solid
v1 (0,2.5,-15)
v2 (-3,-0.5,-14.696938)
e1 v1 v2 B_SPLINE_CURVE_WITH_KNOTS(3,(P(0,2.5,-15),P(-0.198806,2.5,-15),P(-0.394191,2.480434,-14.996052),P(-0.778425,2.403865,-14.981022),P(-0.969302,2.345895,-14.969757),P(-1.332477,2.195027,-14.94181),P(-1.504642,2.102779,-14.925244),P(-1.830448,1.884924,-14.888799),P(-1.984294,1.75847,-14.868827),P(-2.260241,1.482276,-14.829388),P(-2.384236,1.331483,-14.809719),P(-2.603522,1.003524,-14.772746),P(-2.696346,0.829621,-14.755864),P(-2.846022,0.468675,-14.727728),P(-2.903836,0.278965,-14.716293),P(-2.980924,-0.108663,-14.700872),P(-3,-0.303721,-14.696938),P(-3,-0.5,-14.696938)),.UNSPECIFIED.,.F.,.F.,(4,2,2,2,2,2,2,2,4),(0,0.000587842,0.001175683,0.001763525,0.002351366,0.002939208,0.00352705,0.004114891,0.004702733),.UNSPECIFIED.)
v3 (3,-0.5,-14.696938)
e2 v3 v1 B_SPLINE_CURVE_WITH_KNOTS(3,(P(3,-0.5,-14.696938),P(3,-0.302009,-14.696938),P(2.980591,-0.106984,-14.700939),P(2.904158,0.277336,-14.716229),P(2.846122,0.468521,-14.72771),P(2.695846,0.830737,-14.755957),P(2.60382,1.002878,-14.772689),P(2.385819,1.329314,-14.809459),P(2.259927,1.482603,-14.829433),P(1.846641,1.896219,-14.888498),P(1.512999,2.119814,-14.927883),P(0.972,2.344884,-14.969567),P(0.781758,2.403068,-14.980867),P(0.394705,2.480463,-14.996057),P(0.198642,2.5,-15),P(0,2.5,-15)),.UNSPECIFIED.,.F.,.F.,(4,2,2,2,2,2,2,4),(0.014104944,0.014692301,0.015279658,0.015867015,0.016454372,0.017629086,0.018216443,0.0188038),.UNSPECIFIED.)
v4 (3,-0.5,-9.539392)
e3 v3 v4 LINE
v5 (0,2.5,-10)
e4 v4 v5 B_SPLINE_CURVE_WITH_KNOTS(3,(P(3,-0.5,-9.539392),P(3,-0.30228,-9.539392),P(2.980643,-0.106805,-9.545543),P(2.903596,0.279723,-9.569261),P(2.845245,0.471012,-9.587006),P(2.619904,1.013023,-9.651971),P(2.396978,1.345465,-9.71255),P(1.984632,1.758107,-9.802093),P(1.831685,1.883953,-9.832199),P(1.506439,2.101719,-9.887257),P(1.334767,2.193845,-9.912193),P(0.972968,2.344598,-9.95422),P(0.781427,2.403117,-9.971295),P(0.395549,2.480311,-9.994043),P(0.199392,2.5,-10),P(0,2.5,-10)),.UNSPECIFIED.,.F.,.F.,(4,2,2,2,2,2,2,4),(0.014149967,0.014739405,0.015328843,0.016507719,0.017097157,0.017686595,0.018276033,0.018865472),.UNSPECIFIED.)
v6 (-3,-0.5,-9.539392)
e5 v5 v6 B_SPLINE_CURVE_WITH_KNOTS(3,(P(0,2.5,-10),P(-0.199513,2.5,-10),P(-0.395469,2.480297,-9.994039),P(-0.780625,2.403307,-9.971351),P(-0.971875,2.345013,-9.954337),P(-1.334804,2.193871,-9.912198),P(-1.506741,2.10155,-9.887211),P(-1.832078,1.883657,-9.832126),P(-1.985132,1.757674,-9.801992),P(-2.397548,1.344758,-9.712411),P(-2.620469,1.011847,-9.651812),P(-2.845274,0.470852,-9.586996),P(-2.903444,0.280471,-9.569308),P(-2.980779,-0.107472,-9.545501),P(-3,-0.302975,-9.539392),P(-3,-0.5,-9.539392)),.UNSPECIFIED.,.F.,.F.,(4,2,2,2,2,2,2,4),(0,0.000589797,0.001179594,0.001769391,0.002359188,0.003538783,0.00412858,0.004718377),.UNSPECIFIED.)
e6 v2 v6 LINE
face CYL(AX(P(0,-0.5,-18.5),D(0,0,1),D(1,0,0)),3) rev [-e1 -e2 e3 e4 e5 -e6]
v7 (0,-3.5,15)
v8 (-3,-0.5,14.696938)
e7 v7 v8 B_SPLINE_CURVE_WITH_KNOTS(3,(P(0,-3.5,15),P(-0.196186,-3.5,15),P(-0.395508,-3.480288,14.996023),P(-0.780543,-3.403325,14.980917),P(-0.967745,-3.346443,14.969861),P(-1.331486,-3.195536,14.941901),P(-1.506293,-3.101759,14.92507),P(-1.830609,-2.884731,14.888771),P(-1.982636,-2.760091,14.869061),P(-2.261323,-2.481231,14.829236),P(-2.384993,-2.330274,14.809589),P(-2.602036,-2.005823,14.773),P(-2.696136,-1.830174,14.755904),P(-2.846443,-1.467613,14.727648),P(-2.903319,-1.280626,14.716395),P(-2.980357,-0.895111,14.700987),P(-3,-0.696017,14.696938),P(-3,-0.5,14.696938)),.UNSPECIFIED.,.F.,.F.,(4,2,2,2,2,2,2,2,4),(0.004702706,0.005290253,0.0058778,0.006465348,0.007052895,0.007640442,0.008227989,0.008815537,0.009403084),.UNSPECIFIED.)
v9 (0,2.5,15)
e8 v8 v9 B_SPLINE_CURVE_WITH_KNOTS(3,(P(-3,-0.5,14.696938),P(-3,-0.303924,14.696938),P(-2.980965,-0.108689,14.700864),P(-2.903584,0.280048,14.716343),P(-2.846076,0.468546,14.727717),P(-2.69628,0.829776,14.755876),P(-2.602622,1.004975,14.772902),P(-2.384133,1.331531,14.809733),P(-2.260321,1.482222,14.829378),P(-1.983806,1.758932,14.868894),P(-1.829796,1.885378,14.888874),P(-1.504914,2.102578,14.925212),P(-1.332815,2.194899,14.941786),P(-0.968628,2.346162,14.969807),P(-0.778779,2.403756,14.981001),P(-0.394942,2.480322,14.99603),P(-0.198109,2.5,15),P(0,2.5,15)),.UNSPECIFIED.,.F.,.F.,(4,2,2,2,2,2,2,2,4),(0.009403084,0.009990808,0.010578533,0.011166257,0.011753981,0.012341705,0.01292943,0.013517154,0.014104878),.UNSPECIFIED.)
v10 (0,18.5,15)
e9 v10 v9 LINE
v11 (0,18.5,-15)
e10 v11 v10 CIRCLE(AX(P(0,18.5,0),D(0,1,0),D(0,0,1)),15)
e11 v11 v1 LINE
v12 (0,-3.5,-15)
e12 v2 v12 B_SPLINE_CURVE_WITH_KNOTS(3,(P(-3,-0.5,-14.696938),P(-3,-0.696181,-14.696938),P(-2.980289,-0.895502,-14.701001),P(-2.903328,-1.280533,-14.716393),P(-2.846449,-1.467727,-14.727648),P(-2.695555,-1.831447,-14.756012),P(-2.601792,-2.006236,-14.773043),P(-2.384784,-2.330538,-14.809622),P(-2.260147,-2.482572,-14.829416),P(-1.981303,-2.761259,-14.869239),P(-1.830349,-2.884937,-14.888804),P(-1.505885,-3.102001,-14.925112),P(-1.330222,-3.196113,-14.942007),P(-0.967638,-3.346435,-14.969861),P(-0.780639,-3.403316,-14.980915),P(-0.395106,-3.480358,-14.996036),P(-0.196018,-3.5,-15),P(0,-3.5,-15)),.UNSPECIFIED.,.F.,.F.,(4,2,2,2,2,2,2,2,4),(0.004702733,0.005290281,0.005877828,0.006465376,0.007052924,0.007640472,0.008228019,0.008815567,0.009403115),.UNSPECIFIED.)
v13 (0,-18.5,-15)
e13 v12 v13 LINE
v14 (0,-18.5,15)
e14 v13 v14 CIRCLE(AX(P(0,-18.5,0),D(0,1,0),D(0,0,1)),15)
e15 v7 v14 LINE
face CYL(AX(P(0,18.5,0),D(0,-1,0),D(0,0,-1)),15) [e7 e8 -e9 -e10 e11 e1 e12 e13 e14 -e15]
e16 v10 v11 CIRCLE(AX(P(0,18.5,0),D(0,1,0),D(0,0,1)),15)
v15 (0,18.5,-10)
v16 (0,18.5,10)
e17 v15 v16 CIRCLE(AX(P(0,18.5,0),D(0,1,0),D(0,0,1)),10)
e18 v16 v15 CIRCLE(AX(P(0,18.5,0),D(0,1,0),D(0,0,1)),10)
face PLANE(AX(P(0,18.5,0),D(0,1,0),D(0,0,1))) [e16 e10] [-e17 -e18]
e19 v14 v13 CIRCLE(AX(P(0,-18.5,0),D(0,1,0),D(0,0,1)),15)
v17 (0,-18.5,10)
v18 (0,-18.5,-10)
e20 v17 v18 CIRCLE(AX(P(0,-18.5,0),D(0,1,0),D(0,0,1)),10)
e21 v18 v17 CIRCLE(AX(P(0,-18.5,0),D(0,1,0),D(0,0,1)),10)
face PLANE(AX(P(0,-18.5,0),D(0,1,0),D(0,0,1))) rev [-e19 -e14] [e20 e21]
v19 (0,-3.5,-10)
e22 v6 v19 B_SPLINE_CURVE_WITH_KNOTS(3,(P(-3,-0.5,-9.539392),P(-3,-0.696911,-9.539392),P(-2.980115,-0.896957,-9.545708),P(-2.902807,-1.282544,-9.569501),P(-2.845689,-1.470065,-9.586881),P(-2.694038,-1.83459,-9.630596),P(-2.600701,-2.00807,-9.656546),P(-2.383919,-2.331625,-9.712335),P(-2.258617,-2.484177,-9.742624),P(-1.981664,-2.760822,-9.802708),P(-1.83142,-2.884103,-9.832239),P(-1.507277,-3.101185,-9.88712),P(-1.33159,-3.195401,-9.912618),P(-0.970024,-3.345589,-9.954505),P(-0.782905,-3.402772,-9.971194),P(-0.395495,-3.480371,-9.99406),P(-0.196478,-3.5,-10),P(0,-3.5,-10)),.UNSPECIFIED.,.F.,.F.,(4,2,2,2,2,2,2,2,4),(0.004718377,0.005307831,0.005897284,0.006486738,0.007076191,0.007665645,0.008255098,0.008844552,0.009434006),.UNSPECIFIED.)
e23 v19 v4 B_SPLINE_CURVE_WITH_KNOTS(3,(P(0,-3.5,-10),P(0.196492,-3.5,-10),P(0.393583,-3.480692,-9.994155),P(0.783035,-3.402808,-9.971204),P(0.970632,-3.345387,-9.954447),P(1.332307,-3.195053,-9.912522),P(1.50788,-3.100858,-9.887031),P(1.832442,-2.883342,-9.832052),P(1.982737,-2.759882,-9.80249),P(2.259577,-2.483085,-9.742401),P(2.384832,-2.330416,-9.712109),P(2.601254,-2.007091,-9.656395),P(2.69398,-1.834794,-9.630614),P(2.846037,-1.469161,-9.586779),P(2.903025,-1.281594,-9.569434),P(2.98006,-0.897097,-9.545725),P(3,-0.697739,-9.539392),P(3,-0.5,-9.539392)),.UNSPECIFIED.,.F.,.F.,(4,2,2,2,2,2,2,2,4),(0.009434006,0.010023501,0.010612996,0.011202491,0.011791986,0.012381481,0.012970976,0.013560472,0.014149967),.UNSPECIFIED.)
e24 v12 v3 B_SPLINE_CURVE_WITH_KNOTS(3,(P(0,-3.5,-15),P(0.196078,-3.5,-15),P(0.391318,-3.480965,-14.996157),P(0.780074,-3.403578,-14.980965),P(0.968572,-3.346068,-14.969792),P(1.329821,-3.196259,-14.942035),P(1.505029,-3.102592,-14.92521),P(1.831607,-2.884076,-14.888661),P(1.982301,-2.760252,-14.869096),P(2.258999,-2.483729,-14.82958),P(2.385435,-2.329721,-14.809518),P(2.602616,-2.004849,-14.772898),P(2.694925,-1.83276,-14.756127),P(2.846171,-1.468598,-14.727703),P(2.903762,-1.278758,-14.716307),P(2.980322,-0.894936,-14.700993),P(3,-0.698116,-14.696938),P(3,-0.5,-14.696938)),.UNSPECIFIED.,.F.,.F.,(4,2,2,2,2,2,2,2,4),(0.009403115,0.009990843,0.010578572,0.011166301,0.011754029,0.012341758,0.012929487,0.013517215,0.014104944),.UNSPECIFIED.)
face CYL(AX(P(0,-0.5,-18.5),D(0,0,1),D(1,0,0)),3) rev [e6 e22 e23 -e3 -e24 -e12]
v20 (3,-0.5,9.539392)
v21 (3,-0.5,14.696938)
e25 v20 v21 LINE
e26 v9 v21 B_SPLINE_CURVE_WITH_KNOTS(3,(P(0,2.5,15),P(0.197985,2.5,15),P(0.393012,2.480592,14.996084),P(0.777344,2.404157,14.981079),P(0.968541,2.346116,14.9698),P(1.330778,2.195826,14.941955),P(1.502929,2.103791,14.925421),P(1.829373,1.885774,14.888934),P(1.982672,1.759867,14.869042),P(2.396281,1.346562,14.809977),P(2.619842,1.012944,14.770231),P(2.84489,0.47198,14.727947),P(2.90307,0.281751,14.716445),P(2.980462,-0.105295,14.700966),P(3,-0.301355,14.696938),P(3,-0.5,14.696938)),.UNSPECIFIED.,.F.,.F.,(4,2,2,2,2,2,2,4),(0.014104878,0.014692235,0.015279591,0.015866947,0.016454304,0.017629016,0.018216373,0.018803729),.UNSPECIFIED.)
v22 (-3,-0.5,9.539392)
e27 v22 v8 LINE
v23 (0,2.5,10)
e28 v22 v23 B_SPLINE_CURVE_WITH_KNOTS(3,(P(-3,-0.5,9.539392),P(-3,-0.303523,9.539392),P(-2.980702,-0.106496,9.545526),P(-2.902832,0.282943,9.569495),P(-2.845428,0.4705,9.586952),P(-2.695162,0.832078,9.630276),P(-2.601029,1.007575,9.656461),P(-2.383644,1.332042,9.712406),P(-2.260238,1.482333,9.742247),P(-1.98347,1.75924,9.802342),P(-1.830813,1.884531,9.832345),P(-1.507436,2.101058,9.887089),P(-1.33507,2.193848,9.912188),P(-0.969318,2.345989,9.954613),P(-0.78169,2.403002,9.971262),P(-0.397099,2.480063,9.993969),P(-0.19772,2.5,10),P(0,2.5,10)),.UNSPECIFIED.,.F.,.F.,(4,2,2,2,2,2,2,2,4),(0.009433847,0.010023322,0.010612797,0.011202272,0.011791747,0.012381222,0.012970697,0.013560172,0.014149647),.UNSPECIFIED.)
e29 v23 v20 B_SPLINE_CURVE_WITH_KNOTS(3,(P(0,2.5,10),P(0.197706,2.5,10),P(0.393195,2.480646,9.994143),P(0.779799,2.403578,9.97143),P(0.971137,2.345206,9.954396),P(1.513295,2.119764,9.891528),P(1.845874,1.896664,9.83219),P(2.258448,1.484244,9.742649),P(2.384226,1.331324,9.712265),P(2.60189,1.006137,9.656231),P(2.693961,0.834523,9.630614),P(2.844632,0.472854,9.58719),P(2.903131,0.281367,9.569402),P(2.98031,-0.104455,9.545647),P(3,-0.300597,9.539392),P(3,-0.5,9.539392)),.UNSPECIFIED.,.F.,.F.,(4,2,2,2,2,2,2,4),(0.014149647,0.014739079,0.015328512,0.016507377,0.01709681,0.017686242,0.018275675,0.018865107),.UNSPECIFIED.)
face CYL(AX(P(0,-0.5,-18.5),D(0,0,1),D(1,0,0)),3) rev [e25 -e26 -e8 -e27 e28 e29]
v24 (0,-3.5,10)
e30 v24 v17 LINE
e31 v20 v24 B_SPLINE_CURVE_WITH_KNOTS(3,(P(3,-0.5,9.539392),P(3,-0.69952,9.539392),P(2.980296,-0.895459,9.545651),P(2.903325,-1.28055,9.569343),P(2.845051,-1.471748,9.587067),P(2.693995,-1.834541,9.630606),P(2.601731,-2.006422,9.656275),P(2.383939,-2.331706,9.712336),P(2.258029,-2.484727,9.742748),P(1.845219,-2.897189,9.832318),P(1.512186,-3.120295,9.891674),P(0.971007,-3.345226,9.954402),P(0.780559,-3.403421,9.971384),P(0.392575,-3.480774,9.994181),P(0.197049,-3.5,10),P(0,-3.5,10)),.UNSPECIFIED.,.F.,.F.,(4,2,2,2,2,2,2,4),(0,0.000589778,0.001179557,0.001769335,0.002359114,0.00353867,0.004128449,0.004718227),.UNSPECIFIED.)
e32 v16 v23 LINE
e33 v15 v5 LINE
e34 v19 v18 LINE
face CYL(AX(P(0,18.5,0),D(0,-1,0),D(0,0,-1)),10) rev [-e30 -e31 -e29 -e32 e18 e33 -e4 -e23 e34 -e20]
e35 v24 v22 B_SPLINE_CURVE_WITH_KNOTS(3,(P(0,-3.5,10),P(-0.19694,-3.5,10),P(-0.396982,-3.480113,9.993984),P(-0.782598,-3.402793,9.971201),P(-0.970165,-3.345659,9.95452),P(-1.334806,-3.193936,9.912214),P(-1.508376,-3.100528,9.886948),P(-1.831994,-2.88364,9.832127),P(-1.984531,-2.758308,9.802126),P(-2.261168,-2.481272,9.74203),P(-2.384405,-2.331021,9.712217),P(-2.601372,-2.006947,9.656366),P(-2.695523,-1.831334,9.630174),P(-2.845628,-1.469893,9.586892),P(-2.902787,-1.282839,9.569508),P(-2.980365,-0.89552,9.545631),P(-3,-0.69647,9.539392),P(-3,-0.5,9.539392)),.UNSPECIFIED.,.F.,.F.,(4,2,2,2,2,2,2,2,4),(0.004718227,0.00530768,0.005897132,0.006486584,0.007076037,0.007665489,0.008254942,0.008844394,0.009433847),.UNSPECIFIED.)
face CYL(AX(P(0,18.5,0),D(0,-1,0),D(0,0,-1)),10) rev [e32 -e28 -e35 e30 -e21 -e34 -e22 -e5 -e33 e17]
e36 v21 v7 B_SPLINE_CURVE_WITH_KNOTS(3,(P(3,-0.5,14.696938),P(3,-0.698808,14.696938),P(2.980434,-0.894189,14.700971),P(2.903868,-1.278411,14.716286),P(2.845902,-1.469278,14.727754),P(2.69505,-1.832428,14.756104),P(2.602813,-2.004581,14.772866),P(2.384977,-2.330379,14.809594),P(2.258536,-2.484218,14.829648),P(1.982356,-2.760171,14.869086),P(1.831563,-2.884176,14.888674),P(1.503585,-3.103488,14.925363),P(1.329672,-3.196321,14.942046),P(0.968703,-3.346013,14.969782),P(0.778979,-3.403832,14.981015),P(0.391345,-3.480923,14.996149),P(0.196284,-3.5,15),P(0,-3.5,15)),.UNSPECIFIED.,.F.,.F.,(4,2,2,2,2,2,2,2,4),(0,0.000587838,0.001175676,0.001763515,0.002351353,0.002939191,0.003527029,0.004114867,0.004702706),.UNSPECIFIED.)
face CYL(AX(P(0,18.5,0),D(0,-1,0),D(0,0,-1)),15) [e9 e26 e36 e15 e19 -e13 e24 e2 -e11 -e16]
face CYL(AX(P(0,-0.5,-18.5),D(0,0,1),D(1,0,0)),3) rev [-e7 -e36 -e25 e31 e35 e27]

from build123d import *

# Parameters (mm, degrees)
BUSH_RING_PROFILE_SKETCH_R   = 15
BUSH_RING_PROFILE_SKETCH_R_2 = 10
BUSH_BODY_30X_20X37_DEPTH    = 18.5
CROSS_HOLE_SKETCH_R          = 3
CROSS_HOLE_6_DEPTH           = 18.5


with BuildPart() as part:
    # Bush Ring Profile Sketch → Bush Body Ø30xØ20x37 (new, symmetric)
    with BuildSketch(Plane(origin=(0, 0, 0), x_dir=(1, 0, 0), z_dir=(0, 1, 0))):
        with Locations(Location((0, 0, 0), (0, 0, 270))):
            Circle(BUSH_RING_PROFILE_SKETCH_R)
        with Locations(Location((0, 0, 0), (0, 0, 270))):
            Circle(BUSH_RING_PROFILE_SKETCH_R_2, mode=Mode.SUBTRACT)
    extrude(amount=BUSH_BODY_30X_20X37_DEPTH, both=True)

    # Cross Hole Sketch → Cross Hole Ø6 (cut, symmetric)
    with BuildSketch(Plane.XY):
        with Locations((0, -0.5)):
            Circle(CROSS_HOLE_SKETCH_R)
    extrude(amount=CROSS_HOLE_6_DEPTH, both=True, mode=Mode.SUBTRACT)


solid = part.part
